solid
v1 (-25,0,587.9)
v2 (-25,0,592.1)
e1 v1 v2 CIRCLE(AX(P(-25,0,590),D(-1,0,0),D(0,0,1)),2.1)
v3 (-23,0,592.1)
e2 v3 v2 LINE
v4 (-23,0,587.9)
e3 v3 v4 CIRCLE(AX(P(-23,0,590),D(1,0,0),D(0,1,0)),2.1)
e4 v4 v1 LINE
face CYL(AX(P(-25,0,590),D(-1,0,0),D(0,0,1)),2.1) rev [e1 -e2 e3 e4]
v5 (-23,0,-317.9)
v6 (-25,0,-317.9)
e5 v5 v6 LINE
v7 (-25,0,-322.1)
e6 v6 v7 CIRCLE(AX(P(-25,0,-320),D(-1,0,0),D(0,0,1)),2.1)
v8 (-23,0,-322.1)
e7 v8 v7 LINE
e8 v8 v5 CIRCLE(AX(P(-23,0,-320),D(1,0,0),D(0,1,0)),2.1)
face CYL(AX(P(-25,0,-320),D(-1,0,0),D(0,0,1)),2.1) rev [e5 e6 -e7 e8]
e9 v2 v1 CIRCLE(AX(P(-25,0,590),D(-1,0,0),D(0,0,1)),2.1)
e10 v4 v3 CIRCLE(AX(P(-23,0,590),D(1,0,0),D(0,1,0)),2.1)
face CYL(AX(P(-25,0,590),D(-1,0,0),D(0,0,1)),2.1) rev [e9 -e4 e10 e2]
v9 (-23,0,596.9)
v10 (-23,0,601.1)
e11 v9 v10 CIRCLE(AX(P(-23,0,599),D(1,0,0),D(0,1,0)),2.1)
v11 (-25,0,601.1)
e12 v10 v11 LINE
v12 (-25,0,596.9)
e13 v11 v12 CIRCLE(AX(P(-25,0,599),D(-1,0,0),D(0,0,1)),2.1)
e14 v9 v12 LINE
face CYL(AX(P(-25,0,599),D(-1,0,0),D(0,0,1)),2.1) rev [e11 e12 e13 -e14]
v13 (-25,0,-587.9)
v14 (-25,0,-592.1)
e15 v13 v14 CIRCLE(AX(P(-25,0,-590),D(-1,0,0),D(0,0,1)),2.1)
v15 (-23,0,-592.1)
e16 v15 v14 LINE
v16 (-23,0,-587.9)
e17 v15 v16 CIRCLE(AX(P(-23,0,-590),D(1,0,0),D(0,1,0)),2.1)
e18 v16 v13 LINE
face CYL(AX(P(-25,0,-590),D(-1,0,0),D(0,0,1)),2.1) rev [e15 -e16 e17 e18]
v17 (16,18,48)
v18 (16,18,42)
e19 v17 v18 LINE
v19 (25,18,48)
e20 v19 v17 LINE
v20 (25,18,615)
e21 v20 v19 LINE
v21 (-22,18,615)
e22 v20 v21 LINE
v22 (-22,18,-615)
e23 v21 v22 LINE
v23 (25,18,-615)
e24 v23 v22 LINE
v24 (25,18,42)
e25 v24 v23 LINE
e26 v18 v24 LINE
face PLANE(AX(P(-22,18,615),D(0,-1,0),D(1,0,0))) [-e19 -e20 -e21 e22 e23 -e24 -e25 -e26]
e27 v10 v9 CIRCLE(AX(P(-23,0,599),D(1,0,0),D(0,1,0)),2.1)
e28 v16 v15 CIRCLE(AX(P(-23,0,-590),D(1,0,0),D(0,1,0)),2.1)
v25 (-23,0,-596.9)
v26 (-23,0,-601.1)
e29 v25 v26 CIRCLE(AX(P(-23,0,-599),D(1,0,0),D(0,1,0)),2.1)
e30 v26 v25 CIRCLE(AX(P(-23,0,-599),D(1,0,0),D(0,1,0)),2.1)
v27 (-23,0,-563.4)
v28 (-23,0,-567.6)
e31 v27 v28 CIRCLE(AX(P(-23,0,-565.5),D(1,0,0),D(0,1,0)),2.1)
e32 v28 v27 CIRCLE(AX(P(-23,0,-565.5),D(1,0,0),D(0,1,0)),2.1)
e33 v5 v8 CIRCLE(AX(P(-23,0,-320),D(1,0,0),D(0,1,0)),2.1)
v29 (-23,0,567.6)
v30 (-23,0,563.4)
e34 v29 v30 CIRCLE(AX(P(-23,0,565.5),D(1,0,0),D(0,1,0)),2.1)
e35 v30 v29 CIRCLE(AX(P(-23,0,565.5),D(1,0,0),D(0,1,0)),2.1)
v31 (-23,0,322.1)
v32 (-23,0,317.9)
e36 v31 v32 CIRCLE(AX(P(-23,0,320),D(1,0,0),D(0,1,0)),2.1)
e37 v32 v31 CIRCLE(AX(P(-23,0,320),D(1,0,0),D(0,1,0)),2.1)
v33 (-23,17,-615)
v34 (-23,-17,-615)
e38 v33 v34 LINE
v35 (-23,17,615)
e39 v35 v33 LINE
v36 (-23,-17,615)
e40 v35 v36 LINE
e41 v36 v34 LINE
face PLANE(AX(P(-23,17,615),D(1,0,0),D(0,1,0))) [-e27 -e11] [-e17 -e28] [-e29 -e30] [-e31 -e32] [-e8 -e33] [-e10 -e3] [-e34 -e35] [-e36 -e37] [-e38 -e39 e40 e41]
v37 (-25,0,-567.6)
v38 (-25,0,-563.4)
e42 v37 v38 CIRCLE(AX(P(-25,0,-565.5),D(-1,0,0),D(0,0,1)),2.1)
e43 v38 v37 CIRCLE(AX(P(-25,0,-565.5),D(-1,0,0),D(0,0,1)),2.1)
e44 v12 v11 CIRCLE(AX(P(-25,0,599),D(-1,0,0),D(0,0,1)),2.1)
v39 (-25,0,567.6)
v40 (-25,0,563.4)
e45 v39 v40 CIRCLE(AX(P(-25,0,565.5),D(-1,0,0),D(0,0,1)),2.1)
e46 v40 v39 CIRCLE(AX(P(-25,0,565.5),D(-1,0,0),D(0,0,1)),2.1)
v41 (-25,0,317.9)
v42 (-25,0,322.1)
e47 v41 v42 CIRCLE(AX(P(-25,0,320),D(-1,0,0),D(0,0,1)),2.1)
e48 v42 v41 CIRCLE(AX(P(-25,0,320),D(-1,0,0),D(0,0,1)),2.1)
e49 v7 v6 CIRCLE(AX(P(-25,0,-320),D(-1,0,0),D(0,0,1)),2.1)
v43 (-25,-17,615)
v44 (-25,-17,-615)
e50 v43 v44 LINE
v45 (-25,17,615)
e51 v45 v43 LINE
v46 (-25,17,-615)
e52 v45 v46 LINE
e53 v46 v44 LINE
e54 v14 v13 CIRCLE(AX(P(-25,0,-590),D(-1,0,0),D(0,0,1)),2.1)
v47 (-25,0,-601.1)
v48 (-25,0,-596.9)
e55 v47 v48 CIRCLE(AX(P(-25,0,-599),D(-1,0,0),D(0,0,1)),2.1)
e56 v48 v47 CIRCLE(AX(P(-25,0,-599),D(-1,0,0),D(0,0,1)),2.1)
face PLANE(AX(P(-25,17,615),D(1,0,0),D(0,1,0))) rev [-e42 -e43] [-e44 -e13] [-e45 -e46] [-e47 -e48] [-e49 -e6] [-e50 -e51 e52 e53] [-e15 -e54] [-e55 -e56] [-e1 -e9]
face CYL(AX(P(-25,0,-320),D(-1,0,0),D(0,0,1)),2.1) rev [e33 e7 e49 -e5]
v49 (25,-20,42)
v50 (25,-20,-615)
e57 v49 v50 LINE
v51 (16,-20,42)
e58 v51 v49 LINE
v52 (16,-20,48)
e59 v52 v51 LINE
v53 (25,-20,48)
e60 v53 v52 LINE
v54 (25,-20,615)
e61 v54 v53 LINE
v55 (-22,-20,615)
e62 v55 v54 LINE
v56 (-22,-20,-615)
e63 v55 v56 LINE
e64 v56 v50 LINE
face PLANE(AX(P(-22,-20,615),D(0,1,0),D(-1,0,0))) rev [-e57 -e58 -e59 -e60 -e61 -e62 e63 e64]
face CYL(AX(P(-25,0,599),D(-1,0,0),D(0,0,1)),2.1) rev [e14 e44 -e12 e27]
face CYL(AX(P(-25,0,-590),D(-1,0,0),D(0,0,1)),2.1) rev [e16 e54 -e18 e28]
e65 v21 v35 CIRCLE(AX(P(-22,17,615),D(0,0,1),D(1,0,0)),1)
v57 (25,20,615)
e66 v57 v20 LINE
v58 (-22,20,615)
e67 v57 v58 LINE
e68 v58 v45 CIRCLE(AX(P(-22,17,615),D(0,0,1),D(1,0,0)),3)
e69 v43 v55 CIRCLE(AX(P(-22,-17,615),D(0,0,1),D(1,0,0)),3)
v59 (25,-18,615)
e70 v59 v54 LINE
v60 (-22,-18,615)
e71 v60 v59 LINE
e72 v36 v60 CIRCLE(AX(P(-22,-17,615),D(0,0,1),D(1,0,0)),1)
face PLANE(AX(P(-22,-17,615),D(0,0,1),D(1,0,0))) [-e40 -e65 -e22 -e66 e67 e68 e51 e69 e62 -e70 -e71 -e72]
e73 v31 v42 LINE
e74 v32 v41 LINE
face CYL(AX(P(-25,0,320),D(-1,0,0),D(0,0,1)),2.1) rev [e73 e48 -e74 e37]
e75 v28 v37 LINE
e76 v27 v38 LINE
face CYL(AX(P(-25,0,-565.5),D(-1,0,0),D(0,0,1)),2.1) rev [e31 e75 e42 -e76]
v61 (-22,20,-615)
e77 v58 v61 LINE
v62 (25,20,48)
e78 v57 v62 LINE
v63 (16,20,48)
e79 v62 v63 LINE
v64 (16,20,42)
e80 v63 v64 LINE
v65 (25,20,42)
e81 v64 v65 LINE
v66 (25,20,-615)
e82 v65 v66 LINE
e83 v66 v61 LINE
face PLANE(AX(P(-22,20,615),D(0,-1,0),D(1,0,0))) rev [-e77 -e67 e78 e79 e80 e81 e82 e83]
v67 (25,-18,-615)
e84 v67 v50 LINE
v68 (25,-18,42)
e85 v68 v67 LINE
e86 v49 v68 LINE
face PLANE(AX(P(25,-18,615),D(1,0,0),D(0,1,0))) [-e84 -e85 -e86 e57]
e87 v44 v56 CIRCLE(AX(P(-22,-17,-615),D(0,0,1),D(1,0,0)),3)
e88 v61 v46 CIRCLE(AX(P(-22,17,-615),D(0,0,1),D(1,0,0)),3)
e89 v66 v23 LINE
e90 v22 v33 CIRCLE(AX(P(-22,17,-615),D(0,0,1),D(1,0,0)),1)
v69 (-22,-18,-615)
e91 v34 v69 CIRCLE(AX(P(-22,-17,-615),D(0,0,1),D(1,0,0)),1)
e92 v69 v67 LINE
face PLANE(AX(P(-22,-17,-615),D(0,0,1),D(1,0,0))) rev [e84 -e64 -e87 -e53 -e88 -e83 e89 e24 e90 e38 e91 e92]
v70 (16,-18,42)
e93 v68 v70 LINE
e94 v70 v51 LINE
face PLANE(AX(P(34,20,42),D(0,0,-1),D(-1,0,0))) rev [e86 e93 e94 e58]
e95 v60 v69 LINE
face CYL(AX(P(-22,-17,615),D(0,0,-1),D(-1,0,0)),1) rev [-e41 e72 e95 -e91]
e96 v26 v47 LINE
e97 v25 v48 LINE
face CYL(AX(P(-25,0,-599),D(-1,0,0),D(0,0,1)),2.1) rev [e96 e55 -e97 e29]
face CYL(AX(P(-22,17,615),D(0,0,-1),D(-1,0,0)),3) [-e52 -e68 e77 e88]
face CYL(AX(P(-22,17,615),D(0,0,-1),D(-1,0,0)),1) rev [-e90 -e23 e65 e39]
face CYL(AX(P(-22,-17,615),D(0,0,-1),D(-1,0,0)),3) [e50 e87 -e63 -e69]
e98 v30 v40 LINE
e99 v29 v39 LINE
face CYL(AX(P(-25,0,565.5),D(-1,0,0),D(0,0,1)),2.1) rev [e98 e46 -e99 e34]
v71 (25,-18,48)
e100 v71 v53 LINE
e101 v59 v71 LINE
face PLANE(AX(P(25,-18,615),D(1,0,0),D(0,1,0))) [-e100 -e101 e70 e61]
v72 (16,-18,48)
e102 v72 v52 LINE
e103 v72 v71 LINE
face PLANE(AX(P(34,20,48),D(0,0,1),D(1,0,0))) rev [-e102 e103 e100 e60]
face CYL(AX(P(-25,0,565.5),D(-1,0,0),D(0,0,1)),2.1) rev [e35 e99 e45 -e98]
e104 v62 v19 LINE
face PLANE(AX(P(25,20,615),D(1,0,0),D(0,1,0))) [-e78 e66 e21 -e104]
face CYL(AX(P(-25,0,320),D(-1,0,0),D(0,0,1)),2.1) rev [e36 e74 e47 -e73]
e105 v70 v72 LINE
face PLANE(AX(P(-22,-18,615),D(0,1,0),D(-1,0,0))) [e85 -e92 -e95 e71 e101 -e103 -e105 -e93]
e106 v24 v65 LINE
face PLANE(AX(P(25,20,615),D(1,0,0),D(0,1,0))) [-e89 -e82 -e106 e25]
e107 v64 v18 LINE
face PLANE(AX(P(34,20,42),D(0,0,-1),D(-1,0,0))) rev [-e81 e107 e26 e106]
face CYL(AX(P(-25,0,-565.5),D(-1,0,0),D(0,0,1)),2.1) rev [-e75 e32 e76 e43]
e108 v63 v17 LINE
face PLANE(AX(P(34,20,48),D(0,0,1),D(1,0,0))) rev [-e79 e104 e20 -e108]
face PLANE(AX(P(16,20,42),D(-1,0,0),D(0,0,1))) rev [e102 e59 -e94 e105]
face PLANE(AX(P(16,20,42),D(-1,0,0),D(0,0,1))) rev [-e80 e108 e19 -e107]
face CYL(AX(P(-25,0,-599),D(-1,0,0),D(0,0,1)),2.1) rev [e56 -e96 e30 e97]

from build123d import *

# Parameters (mm, degrees)
EXTRUDE_1_DEPTH     = 615
SKETCH_2_W          = 18
SKETCH_2_H          = 6
CUT_EXTRUDE_1_DEPTH = 617.8062905
HOLE_WIZARD_M5_1_D  = 4.2


with BuildPart() as part:
    # 草图1 → 拉伸-薄壁1 (new, symmetric)
    with BuildSketch(Plane.XY):
        with BuildLine():
            Line((25, -20), (-22, -20))
            ThreePointArc((-22, -20), (-24.121320344, -19.121320344), (-25, -17))
            Line((-25, -17), (-25, 17))
            ThreePointArc((-25, 17), (-24.121320344, 19.121320344), (-22, 20))
            Line((-22, 20), (25, 20))
            Line((25, 20), (25, 18))
            Line((25, 18), (-22, 18))
            ThreePointArc((-22, 18), (-22.707106781, 17.707106781), (-23, 17))
            Line((-23, 17), (-23, -17))
            ThreePointArc((-23, -17), (-22.707106781, -17.707106781), (-22, -18))
            Line((-22, -18), (25, -18))
            Line((25, -18), (25, -20))
        make_face()
    extrude(amount=EXTRUDE_1_DEPTH, both=True)

    # 草图2 → 切除-拉伸1 (cut, through all)
    with BuildSketch(Plane.XZ.offset(20)):
        with Locations((25, 45)):
            Rectangle(SKETCH_2_W, SKETCH_2_H)
    extrude(amount=-CUT_EXTRUDE_1_DEPTH, mode=Mode.SUBTRACT)

    # M5 螺纹孔1 (through all)
    with Locations(Plane.ZY.offset(25)):
        with Locations((590, 0), (320, 0), (-320, 0), (-590, 0), (565.5, 0), (599, 0), (-599, 0), (-565.5, 0)):
            Hole(HOLE_WIZARD_M5_1_D / 2)


solid = part.part
